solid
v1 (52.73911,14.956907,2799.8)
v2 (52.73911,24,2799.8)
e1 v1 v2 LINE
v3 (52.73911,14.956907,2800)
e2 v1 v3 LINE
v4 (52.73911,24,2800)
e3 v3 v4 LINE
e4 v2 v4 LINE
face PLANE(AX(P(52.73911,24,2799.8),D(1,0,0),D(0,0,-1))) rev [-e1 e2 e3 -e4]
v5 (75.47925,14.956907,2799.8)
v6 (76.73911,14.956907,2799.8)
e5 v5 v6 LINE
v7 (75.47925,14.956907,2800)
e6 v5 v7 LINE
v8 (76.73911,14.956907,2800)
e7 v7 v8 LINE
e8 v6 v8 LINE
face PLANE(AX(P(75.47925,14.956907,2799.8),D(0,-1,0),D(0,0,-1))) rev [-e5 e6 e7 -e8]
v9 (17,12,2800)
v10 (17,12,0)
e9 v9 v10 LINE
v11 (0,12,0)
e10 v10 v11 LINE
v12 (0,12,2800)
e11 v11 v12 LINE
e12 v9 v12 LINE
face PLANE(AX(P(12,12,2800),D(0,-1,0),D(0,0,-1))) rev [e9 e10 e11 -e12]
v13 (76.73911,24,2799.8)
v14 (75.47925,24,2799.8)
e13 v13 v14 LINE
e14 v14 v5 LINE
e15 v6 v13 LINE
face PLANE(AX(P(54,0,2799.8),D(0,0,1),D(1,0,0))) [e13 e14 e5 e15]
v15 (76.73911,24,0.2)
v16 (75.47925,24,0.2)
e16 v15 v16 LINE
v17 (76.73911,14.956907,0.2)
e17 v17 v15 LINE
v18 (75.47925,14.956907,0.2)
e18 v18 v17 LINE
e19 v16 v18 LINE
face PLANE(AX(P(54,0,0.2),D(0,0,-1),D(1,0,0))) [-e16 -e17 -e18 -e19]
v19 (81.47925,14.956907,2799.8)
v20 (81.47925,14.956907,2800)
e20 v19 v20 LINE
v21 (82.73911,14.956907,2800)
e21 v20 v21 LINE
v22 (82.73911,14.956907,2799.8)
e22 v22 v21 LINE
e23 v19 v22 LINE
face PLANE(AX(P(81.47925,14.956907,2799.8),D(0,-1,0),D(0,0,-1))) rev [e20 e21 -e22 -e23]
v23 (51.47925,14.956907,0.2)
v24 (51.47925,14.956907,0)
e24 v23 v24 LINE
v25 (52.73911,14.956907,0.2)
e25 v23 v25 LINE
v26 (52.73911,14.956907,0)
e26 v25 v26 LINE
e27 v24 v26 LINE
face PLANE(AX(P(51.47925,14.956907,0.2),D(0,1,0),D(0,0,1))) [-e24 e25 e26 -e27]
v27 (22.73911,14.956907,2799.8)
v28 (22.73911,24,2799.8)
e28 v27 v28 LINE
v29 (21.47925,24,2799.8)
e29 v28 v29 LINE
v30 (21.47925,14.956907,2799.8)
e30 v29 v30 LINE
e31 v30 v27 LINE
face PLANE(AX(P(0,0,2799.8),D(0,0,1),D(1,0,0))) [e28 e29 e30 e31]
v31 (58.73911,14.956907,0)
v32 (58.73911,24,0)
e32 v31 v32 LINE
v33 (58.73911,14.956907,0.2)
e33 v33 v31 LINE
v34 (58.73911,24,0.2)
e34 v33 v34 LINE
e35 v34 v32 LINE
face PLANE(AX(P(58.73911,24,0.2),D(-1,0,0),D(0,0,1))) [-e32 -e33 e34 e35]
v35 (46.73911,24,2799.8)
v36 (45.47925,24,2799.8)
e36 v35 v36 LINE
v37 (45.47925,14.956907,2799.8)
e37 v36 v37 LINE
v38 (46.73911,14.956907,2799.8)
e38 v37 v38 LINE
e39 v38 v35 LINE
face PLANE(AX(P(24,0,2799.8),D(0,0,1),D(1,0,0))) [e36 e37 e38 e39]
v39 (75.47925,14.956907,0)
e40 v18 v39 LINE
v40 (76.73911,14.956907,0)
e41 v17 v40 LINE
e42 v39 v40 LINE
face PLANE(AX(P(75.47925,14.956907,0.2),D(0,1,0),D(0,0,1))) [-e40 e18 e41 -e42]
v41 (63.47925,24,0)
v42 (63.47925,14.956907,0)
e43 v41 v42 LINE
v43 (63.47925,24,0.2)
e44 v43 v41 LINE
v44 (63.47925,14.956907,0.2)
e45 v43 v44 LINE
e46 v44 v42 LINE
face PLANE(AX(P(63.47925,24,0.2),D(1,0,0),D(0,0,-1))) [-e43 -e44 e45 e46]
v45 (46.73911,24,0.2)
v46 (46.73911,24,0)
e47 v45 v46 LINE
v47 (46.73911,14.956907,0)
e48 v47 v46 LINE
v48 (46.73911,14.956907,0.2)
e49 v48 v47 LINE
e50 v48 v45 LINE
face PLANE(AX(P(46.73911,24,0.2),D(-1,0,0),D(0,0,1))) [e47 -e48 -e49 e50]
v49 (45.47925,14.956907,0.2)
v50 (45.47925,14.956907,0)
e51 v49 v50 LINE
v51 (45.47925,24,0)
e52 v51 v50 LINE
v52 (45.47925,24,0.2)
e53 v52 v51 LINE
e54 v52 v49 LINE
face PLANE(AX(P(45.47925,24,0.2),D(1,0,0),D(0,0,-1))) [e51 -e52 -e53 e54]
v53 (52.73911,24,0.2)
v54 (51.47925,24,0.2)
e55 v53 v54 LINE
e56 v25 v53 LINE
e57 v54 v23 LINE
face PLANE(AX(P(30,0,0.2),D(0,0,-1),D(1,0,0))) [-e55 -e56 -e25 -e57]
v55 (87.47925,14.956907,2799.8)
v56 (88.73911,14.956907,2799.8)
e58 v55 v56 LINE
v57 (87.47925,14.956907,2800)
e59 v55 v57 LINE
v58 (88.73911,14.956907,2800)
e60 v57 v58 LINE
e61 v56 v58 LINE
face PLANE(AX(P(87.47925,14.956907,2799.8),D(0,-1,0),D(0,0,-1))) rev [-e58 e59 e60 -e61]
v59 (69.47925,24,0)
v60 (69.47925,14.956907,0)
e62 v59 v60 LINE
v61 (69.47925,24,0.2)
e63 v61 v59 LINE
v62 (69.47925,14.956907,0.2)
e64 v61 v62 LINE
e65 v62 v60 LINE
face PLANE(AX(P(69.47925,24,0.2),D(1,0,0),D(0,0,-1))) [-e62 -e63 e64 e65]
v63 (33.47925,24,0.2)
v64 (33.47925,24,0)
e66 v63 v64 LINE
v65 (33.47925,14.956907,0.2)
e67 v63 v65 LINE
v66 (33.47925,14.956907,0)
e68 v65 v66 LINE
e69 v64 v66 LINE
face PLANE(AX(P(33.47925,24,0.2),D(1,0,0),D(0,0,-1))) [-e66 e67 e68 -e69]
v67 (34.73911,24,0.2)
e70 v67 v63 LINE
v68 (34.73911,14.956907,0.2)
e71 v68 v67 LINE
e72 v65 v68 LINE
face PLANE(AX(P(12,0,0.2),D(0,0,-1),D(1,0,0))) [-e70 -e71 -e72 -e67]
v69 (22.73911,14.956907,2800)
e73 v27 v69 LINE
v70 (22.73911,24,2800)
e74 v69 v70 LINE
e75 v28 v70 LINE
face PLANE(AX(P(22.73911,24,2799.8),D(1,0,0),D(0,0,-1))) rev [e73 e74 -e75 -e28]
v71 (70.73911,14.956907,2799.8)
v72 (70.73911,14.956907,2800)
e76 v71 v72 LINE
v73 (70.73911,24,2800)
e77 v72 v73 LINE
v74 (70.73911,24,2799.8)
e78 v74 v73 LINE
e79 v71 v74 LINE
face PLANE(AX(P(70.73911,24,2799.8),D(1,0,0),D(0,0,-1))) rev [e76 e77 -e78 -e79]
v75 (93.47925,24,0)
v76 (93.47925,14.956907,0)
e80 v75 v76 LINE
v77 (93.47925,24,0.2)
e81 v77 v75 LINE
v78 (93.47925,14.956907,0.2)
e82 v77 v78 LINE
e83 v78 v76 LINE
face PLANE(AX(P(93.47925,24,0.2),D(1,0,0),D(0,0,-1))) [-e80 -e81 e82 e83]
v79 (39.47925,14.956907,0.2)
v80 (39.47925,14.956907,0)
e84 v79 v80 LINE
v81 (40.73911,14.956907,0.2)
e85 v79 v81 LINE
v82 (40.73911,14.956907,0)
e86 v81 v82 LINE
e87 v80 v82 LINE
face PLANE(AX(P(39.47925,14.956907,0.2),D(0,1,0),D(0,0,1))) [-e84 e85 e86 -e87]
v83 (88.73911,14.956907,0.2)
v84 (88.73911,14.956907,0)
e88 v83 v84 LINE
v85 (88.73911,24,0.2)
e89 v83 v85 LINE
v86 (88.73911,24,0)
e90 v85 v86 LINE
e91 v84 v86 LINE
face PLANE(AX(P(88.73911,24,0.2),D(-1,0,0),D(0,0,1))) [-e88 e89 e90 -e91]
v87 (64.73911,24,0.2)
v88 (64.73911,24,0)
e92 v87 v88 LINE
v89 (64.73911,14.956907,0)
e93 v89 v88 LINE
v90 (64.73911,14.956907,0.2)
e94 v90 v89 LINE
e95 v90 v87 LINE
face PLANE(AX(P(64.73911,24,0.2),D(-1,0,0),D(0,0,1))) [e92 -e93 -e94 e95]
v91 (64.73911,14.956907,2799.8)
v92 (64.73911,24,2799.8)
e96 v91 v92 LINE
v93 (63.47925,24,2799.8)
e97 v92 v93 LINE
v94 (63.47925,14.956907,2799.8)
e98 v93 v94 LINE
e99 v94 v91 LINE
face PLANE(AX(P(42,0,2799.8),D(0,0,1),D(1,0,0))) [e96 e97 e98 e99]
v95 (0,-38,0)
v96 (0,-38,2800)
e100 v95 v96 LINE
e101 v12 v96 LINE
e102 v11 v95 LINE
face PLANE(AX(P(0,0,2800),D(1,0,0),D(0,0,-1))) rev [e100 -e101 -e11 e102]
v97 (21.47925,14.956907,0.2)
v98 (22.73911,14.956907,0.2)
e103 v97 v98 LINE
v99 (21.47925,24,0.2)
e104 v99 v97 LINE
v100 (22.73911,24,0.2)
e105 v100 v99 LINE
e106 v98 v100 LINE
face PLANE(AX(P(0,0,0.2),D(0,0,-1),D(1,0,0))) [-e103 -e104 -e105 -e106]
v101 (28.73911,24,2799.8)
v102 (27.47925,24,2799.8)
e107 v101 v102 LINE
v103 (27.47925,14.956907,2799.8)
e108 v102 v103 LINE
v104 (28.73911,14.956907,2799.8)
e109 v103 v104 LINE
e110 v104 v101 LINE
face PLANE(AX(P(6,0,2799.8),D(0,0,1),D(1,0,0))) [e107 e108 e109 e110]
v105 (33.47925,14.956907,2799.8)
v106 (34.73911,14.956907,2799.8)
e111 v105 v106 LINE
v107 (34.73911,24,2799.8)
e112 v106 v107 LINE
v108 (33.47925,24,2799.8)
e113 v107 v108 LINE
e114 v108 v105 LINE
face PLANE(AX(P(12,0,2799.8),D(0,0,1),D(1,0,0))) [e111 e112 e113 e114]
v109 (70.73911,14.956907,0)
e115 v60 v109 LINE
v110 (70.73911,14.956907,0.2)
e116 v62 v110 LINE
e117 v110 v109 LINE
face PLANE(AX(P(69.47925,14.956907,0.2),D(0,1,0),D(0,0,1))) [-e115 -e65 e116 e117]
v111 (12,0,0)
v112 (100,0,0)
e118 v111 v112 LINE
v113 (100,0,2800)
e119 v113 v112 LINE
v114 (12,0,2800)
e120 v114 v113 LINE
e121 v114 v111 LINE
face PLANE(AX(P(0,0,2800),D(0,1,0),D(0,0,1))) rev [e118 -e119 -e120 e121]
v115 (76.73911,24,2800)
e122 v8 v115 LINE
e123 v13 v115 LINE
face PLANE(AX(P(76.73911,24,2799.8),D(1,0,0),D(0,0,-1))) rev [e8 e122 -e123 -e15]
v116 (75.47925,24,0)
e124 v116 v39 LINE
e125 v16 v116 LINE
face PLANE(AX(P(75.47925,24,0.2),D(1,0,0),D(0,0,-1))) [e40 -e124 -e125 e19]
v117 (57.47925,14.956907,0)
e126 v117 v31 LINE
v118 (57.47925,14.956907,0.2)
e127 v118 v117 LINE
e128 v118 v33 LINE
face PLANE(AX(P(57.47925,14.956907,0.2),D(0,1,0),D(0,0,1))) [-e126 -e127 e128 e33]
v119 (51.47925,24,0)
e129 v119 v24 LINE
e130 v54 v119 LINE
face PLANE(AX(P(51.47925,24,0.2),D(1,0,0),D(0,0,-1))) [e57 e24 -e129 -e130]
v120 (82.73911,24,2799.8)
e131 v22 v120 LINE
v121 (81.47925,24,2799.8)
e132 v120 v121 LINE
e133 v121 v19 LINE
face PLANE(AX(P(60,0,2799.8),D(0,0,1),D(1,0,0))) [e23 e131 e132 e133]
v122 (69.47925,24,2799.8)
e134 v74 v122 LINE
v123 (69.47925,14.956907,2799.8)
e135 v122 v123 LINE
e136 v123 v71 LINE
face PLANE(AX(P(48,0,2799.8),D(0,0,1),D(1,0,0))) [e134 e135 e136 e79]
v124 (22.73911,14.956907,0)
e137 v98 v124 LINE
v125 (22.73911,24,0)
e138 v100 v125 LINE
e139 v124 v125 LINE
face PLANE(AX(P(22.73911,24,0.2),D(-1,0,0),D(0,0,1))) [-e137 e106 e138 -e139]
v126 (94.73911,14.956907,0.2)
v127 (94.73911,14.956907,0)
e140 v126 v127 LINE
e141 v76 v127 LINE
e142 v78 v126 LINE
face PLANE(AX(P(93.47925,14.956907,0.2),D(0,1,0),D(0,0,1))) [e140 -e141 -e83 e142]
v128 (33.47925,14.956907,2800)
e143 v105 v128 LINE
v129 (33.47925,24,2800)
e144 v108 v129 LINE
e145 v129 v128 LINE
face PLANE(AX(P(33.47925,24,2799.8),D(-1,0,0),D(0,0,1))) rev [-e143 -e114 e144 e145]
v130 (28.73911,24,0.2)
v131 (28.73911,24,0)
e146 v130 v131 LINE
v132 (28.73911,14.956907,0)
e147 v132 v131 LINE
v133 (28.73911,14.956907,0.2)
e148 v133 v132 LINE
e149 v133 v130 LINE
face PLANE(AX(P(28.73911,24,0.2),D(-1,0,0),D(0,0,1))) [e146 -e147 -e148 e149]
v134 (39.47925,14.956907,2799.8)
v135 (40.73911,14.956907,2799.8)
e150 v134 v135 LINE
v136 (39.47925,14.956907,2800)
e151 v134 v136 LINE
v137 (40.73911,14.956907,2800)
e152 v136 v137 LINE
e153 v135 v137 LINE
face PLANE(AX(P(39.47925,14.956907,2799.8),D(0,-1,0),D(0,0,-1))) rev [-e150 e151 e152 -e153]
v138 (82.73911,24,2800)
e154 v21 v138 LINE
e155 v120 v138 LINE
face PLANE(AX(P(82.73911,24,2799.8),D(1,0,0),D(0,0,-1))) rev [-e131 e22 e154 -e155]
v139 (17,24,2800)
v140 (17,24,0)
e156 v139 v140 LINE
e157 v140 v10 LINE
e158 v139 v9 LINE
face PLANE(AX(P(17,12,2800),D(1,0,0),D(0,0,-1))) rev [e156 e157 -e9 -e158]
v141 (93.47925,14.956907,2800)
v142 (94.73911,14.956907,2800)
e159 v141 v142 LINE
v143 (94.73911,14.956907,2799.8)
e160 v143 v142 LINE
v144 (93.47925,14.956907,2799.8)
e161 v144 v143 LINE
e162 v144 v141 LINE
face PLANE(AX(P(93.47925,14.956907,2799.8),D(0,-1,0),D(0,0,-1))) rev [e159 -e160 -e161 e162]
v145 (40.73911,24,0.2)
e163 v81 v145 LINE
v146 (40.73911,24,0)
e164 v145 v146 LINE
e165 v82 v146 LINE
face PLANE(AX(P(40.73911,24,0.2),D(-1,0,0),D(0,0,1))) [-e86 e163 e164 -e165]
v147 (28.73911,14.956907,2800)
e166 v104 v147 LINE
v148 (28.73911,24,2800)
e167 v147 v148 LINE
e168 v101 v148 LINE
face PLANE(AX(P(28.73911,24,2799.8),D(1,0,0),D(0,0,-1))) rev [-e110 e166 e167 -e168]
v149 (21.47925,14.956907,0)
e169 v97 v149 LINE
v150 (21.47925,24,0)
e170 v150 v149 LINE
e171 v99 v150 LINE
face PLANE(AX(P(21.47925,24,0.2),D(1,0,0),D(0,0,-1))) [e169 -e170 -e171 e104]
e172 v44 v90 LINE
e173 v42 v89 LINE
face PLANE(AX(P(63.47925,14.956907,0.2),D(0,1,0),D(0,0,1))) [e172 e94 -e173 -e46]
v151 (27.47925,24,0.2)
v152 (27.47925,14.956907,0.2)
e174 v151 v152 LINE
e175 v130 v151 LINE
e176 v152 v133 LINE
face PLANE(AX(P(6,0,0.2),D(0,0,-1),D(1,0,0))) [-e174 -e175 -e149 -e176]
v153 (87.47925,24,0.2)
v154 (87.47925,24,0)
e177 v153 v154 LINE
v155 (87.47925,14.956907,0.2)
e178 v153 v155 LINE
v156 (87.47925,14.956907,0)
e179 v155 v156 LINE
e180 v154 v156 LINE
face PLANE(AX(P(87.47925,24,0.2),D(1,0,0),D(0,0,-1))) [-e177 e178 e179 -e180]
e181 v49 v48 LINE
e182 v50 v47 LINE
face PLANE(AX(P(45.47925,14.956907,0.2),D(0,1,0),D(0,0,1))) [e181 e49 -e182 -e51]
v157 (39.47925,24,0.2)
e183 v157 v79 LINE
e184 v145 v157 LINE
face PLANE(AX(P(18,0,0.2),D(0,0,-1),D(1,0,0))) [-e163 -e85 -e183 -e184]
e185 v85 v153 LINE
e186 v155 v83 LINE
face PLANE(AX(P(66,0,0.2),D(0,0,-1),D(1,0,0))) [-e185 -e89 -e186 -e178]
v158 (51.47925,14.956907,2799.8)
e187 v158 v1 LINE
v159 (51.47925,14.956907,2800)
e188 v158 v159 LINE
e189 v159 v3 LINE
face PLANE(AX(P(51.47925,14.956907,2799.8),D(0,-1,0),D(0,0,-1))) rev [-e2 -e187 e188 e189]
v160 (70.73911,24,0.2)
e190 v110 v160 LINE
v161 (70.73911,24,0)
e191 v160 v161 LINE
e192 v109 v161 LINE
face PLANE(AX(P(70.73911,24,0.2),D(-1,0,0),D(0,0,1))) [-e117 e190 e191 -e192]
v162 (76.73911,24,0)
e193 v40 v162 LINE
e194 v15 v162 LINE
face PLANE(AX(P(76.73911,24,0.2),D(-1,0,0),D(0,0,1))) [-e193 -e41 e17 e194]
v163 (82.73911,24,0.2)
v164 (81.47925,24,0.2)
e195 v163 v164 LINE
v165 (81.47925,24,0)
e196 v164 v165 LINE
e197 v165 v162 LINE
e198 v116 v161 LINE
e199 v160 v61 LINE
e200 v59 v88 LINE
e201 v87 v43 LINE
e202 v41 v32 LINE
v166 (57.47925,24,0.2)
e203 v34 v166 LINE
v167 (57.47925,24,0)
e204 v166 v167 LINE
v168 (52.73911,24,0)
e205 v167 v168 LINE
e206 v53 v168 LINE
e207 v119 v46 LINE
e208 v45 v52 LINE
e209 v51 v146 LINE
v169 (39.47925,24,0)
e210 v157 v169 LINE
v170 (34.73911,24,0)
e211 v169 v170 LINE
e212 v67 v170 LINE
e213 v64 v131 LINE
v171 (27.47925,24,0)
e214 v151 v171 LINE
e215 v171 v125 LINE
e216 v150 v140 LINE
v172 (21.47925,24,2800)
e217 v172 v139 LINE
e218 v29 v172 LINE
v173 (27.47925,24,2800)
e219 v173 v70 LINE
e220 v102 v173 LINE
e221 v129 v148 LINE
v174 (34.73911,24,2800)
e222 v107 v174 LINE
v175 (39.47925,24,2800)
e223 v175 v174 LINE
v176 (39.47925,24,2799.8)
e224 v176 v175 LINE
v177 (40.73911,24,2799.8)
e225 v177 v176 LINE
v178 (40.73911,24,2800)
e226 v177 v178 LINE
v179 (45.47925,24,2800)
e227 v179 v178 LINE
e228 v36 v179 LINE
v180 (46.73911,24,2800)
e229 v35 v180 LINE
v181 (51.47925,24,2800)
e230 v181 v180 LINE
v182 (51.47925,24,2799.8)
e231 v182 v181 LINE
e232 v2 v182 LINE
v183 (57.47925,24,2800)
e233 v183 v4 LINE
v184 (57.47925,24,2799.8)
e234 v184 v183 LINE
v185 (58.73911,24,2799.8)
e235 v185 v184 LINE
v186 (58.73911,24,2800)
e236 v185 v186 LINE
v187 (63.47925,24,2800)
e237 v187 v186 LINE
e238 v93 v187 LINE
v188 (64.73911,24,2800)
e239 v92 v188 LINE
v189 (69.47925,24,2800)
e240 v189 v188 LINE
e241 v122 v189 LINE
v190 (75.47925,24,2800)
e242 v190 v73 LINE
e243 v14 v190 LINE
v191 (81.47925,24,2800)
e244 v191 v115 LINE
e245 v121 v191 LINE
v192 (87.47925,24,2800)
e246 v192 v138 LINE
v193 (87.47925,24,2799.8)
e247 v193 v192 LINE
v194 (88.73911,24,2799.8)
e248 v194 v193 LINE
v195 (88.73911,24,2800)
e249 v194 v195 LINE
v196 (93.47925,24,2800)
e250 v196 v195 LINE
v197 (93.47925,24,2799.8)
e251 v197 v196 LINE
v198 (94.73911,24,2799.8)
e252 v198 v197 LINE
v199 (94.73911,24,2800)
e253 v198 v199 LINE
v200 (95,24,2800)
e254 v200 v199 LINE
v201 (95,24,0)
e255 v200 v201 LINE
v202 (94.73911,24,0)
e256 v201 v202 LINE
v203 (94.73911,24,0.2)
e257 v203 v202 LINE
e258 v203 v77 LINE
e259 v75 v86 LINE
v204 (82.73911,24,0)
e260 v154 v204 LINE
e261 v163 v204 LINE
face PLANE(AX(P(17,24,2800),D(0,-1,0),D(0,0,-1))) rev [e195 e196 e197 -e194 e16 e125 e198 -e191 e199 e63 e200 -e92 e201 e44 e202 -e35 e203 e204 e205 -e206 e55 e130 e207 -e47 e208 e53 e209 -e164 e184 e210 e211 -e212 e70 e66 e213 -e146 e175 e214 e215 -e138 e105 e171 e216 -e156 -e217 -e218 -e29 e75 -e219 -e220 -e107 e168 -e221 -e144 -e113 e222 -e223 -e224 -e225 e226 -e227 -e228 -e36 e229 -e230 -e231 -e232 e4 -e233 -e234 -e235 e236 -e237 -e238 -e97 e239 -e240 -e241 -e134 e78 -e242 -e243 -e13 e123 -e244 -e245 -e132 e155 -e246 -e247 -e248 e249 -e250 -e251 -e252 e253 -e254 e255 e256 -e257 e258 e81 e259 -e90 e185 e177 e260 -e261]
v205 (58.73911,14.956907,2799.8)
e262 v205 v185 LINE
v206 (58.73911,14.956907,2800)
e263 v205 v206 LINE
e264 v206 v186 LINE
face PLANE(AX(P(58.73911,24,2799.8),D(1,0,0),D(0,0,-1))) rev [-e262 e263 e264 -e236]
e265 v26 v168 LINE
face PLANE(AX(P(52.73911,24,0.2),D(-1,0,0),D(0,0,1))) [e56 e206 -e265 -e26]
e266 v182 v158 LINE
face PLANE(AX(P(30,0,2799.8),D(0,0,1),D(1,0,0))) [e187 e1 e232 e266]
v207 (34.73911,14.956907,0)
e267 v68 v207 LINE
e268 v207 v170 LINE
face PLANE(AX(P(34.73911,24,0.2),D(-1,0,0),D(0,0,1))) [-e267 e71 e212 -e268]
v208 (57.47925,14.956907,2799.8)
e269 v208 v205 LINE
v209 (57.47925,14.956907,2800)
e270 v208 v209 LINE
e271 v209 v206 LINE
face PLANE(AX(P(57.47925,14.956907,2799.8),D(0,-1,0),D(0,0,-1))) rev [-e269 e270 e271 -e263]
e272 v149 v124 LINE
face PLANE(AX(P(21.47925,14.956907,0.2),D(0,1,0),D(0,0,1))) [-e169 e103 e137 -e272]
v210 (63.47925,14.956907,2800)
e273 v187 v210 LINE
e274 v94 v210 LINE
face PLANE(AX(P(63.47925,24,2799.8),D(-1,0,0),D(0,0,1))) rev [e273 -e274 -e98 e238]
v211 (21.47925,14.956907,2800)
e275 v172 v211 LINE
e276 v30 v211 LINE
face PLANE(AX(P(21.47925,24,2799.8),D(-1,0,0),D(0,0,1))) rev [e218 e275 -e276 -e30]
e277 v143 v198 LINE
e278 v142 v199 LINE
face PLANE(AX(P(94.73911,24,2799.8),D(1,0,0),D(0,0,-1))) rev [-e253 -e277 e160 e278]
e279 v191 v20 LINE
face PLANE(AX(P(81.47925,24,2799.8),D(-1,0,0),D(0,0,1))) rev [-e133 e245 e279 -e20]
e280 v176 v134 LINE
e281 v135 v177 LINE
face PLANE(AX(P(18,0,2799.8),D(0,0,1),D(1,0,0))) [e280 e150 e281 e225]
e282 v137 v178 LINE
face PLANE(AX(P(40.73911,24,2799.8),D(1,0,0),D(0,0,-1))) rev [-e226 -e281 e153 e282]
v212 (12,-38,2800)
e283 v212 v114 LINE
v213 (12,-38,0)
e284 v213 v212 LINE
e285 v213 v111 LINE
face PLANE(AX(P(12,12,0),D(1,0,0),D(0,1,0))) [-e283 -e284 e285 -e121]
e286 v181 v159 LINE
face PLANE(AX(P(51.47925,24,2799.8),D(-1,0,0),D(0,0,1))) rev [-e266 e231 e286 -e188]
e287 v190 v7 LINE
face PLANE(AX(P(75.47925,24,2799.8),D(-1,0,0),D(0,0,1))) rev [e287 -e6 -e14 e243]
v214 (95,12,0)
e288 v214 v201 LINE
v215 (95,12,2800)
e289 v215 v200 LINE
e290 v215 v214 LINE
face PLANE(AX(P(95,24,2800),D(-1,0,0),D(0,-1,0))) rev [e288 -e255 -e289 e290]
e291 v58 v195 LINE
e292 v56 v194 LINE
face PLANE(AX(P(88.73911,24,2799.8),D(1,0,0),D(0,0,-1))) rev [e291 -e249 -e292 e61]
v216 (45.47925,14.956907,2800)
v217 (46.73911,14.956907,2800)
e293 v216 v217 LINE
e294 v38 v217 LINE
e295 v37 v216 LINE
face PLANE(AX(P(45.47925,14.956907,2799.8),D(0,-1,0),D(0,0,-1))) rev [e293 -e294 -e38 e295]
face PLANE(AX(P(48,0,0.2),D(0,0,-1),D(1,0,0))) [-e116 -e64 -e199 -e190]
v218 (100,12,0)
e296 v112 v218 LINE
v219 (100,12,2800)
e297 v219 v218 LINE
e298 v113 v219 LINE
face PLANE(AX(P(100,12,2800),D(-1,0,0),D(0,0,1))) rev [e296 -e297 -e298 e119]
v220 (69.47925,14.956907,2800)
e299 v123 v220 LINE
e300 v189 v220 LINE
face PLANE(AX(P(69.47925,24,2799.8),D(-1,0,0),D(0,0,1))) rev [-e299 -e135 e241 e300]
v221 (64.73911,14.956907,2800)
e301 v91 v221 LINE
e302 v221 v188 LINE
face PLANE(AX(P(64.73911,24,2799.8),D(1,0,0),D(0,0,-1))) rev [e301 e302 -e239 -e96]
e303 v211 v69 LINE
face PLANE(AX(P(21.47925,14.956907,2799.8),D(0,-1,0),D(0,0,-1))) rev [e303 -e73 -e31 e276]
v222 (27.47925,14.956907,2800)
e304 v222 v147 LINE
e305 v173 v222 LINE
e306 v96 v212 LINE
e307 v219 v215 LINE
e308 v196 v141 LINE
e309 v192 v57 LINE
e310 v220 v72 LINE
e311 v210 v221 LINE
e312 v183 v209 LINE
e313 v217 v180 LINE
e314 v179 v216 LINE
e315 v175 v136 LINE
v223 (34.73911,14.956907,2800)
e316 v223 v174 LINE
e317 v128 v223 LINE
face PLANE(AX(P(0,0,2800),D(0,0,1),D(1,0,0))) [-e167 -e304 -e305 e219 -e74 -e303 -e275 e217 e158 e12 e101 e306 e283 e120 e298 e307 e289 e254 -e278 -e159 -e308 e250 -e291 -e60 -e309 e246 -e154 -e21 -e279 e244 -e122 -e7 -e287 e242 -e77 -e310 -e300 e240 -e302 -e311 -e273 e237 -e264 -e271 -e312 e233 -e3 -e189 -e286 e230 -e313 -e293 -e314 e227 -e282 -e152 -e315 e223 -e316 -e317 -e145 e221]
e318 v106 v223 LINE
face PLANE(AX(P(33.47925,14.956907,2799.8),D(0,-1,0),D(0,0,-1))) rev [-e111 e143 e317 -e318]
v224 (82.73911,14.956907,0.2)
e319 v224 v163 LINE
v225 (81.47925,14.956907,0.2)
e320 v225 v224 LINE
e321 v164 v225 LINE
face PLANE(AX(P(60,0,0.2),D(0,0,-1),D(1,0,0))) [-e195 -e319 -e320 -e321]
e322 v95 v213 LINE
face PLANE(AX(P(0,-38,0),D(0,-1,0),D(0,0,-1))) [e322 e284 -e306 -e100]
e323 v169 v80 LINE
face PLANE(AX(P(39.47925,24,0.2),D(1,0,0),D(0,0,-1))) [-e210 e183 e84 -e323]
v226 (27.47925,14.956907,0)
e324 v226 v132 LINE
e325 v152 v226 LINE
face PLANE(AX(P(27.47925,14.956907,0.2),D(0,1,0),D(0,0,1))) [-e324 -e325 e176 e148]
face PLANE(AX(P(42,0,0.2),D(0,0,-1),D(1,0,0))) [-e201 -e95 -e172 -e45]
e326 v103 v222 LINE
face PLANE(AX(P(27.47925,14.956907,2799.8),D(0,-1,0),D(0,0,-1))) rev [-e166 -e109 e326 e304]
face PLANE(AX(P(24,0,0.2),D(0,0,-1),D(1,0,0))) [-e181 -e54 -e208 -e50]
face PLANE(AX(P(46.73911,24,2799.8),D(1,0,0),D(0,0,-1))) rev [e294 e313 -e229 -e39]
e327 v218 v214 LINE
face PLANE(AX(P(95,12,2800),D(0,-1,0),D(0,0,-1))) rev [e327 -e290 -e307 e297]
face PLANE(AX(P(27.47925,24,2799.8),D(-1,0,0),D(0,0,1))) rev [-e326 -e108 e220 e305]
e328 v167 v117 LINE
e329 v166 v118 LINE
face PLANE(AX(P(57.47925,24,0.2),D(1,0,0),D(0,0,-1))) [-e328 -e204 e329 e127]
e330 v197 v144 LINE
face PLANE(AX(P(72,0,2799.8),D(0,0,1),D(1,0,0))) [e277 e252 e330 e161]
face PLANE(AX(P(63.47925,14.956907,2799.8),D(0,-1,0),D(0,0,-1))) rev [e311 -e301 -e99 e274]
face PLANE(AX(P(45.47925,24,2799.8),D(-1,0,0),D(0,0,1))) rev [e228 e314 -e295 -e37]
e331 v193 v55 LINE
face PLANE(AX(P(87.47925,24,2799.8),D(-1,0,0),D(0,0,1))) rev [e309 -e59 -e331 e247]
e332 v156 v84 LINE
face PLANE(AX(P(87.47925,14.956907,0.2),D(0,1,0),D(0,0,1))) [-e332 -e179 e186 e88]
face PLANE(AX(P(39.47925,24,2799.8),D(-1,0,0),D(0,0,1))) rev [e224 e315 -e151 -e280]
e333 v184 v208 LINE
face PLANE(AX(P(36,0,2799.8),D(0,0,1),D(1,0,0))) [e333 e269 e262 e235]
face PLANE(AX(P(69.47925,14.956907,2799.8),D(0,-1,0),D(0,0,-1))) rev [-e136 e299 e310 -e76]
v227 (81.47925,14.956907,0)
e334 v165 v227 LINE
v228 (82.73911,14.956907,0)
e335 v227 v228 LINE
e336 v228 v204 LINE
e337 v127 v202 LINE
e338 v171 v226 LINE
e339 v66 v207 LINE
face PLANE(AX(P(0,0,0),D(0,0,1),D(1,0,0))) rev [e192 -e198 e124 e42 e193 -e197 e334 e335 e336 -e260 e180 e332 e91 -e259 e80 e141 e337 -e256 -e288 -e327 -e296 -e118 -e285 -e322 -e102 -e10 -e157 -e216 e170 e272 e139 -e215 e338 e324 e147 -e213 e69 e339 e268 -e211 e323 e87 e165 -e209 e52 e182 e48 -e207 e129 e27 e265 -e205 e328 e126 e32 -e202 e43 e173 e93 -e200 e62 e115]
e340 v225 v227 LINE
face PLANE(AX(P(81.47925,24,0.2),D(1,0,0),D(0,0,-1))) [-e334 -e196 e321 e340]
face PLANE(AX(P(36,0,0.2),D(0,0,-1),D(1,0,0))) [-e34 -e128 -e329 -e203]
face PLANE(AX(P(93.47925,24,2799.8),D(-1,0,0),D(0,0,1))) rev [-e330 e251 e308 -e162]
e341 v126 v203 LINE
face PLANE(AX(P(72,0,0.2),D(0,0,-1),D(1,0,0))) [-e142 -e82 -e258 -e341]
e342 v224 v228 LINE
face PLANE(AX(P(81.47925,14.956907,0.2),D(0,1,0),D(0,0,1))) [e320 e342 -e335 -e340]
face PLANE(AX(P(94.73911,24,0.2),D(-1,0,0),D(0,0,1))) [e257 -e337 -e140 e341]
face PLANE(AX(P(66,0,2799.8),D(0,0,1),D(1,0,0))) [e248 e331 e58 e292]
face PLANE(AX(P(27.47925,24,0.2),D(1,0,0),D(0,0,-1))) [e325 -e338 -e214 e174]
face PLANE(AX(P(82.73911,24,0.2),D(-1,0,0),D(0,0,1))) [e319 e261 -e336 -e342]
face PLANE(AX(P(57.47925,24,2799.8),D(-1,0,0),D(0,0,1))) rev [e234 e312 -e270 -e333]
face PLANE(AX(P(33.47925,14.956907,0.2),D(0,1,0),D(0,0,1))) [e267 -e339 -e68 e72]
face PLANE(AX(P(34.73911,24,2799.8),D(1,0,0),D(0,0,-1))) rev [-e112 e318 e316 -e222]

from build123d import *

# Parameters (mm, degrees)
BOSS_EXTRUDE1_DEPTH      = 2800
SKETCH2_W                = 1.259860676
SKETCH2_H                = 9.043092937
CUT_EXTRUDE1_DEPTH       = 0.2
LPATTERN1_COUNT          = 16
LPATTERN1_PITCH          = 6
MIRROR1_COPY_1_SKETCH_W  = 1.259860676
MIRROR1_COPY_1_SKETCH_H  = 9.043092937
MIRROR1_COPY_1_DEPTH     = 0.2
MIRROR1_COPY_2_SKETCH_W  = 1.259860676
MIRROR1_COPY_2_SKETCH_H  = 9.043092937
MIRROR1_COPY_2_DEPTH     = 0.2
MIRROR1_COPY_3_SKETCH_W  = 1.259860676
MIRROR1_COPY_3_SKETCH_H  = 9.043092937
MIRROR1_COPY_3_DEPTH     = 0.2
MIRROR1_COPY_4_SKETCH_W  = 1.259860676
MIRROR1_COPY_4_SKETCH_H  = 9.043092937
MIRROR1_COPY_4_DEPTH     = 0.2
MIRROR1_COPY_5_SKETCH_W  = 1.259860676
MIRROR1_COPY_5_SKETCH_H  = 9.043092937
MIRROR1_COPY_5_DEPTH     = 0.2
MIRROR1_COPY_6_SKETCH_W  = 1.259860676
MIRROR1_COPY_6_SKETCH_H  = 9.043092937
MIRROR1_COPY_6_DEPTH     = 0.2
MIRROR1_COPY_7_SKETCH_W  = 1.259860676
MIRROR1_COPY_7_SKETCH_H  = 9.043092937
MIRROR1_COPY_7_DEPTH     = 0.2
MIRROR1_COPY_8_SKETCH_W  = 1.259860676
MIRROR1_COPY_8_SKETCH_H  = 9.043092937
MIRROR1_COPY_8_DEPTH     = 0.2
MIRROR1_COPY_9_SKETCH_W  = 1.259860676
MIRROR1_COPY_9_SKETCH_H  = 9.043092937
MIRROR1_COPY_9_DEPTH     = 0.2
MIRROR1_COPY_10_SKETCH_W = 1.259860676
MIRROR1_COPY_10_SKETCH_H = 9.043092937
MIRROR1_COPY_10_DEPTH    = 0.2
MIRROR1_COPY_11_SKETCH_W = 1.259860676
MIRROR1_COPY_11_SKETCH_H = 9.043092937
MIRROR1_COPY_11_DEPTH    = 0.2
MIRROR1_COPY_12_SKETCH_W = 1.259860676
MIRROR1_COPY_12_SKETCH_H = 9.043092937
MIRROR1_COPY_12_DEPTH    = 0.2
MIRROR1_COPY_13_SKETCH_W = 1.259860676
MIRROR1_COPY_13_SKETCH_H = 9.043092937
MIRROR1_COPY_13_DEPTH    = 0.2
MIRROR1_COPY_14_SKETCH_W = 1.259860676
MIRROR1_COPY_14_SKETCH_H = 9.043092937
MIRROR1_COPY_14_DEPTH    = 0.2
MIRROR1_COPY_15_SKETCH_W = 1.259860676
MIRROR1_COPY_15_SKETCH_H = 9.043092937
MIRROR1_COPY_15_DEPTH    = 0.2
SKETCH5_W                = 12
SKETCH5_H                = 50
BOSS_EXTRUDE2_DEPTH      = 2800
SKETCH3_W                = 12
SKETCH3_H                = 88
CUT_EXTRUDE3_DEPTH       = 2804.569153775


with BuildPart() as part:
    # Sketch1 → Boss-Extrude1 (new body)
    with BuildSketch(Plane.XY):
        Polygon((0, 0), (100, 0), (100, 12), (95, 12), (95, 24), (17, 24), (17, 12), (12, 12), (12, 100), (0, 100), align=None)
    extrude(amount=BOSS_EXTRUDE1_DEPTH)

    # Sketch2 → Cut-Extrude1 (cut)
    with BuildSketch(Plane.XY.offset(2800)):
        with Locations((22.109179897, 19.478453532)):
            Rectangle(SKETCH2_W, SKETCH2_H)
    cut_extrude1 = extrude(amount=-CUT_EXTRUDE1_DEPTH, mode=Mode.SUBTRACT)

    # LPattern1: Cut-Extrude1 ×16
    with Locations(*[(i * LPATTERN1_PITCH, 0, 0) for i in range(1, LPATTERN1_COUNT)]):
        add(cut_extrude1, mode=Mode.SUBTRACT)

    # Mirror1: Cut-Extrude1 across plane
    add(cut_extrude1.mirror(Plane(origin=(0, 0, 1400), x_dir=(1, 0, 0), z_dir=(0, 0, -1))), mode=Mode.SUBTRACT)

    # Mirror1 copy 1 sketch → Mirror1 copy 1 (cut)
    with BuildSketch(Plane(origin=(6, 0, 0), x_dir=(1, 0, 0), z_dir=(0, 0, -1))):
        with Locations((22.109179897, -19.478453532)):
            Rectangle(MIRROR1_COPY_1_SKETCH_W, MIRROR1_COPY_1_SKETCH_H)
    extrude(amount=-MIRROR1_COPY_1_DEPTH, mode=Mode.SUBTRACT)

    # Mirror1 copy 2 sketch → Mirror1 copy 2 (cut)
    with BuildSketch(Plane(origin=(12, 0, 0), x_dir=(1, 0, 0), z_dir=(0, 0, -1))):
        with Locations((22.109179897, -19.478453532)):
            Rectangle(MIRROR1_COPY_2_SKETCH_W, MIRROR1_COPY_2_SKETCH_H)
    extrude(amount=-MIRROR1_COPY_2_DEPTH, mode=Mode.SUBTRACT)

    # Mirror1 copy 3 sketch → Mirror1 copy 3 (cut)
    with BuildSketch(Plane(origin=(18, 0, 0), x_dir=(1, 0, 0), z_dir=(0, 0, -1))):
        with Locations((22.109179897, -19.478453532)):
            Rectangle(MIRROR1_COPY_3_SKETCH_W, MIRROR1_COPY_3_SKETCH_H)
    extrude(amount=-MIRROR1_COPY_3_DEPTH, mode=Mode.SUBTRACT)

    # Mirror1 copy 4 sketch → Mirror1 copy 4 (cut)
    with BuildSketch(Plane(origin=(24, 0, 0), x_dir=(1, 0, 0), z_dir=(0, 0, -1))):
        with Locations((22.109179897, -19.478453532)):
            Rectangle(MIRROR1_COPY_4_SKETCH_W, MIRROR1_COPY_4_SKETCH_H)
    extrude(amount=-MIRROR1_COPY_4_DEPTH, mode=Mode.SUBTRACT)

    # Mirror1 copy 5 sketch → Mirror1 copy 5 (cut)
    with BuildSketch(Plane(origin=(30, 0, 0), x_dir=(1, 0, 0), z_dir=(0, 0, -1))):
        with Locations((22.109179897, -19.478453532)):
            Rectangle(MIRROR1_COPY_5_SKETCH_W, MIRROR1_COPY_5_SKETCH_H)
    extrude(amount=-MIRROR1_COPY_5_DEPTH, mode=Mode.SUBTRACT)

    # Mirror1 copy 6 sketch → Mirror1 copy 6 (cut)
    with BuildSketch(Plane(origin=(36, 0, 0), x_dir=(1, 0, 0), z_dir=(0, 0, -1))):
        with Locations((22.109179897, -19.478453532)):
            Rectangle(MIRROR1_COPY_6_SKETCH_W, MIRROR1_COPY_6_SKETCH_H)
    extrude(amount=-MIRROR1_COPY_6_DEPTH, mode=Mode.SUBTRACT)

    # Mirror1 copy 7 sketch → Mirror1 copy 7 (cut)
    with BuildSketch(Plane(origin=(42, 0, 0), x_dir=(1, 0, 0), z_dir=(0, 0, -1))):
        with Locations((22.109179897, -19.478453532)):
            Rectangle(MIRROR1_COPY_7_SKETCH_W, MIRROR1_COPY_7_SKETCH_H)
    extrude(amount=-MIRROR1_COPY_7_DEPTH, mode=Mode.SUBTRACT)

    # Mirror1 copy 8 sketch → Mirror1 copy 8 (cut)
    with BuildSketch(Plane(origin=(48, 0, 0), x_dir=(1, 0, 0), z_dir=(0, 0, -1))):
        with Locations((22.109179897, -19.478453532)):
            Rectangle(MIRROR1_COPY_8_SKETCH_W, MIRROR1_COPY_8_SKETCH_H)
    extrude(amount=-MIRROR1_COPY_8_DEPTH, mode=Mode.SUBTRACT)

    # Mirror1 copy 9 sketch → Mirror1 copy 9 (cut)
    with BuildSketch(Plane(origin=(54, 0, 0), x_dir=(1, 0, 0), z_dir=(0, 0, -1))):
        with Locations((22.109179897, -19.478453532)):
            Rectangle(MIRROR1_COPY_9_SKETCH_W, MIRROR1_COPY_9_SKETCH_H)
    extrude(amount=-MIRROR1_COPY_9_DEPTH, mode=Mode.SUBTRACT)

    # Mirror1 copy 10 sketch → Mirror1 copy 10 (cut)
    with BuildSketch(Plane(origin=(60, 0, 0), x_dir=(1, 0, 0), z_dir=(0, 0, -1))):
        with Locations((22.109179897, -19.478453532)):
            Rectangle(MIRROR1_COPY_10_SKETCH_W, MIRROR1_COPY_10_SKETCH_H)
    extrude(amount=-MIRROR1_COPY_10_DEPTH, mode=Mode.SUBTRACT)

    # Mirror1 copy 11 sketch → Mirror1 copy 11 (cut)
    with BuildSketch(Plane(origin=(66, 0, 0), x_dir=(1, 0, 0), z_dir=(0, 0, -1))):
        with Locations((22.109179897, -19.478453532)):
            Rectangle(MIRROR1_COPY_11_SKETCH_W, MIRROR1_COPY_11_SKETCH_H)
    extrude(amount=-MIRROR1_COPY_11_DEPTH, mode=Mode.SUBTRACT)

    # Mirror1 copy 12 sketch → Mirror1 copy 12 (cut)
    with BuildSketch(Plane(origin=(72, 0, 0), x_dir=(1, 0, 0), z_dir=(0, 0, -1))):
        with Locations((22.109179897, -19.478453532)):
            Rectangle(MIRROR1_COPY_12_SKETCH_W, MIRROR1_COPY_12_SKETCH_H)
    extrude(amount=-MIRROR1_COPY_12_DEPTH, mode=Mode.SUBTRACT)

    # Mirror1 copy 13 sketch → Mirror1 copy 13 (cut)
    with BuildSketch(Plane(origin=(78, 0, 0), x_dir=(1, 0, 0), z_dir=(0, 0, -1))):
        with Locations((22.109179897, -19.478453532)):
            Rectangle(MIRROR1_COPY_13_SKETCH_W, MIRROR1_COPY_13_SKETCH_H)
    extrude(amount=-MIRROR1_COPY_13_DEPTH, mode=Mode.SUBTRACT)

    # Mirror1 copy 14 sketch → Mirror1 copy 14 (cut)
    with BuildSketch(Plane(origin=(84, 0, 0), x_dir=(1, 0, 0), z_dir=(0, 0, -1))):
        with Locations((22.109179897, -19.478453532)):
            Rectangle(MIRROR1_COPY_14_SKETCH_W, MIRROR1_COPY_14_SKETCH_H)
    extrude(amount=-MIRROR1_COPY_14_DEPTH, mode=Mode.SUBTRACT)

    # Mirror1 copy 15 sketch → Mirror1 copy 15 (cut)
    with BuildSketch(Plane(origin=(90, 0, 0), x_dir=(1, 0, 0), z_dir=(0, 0, -1))):
        with Locations((22.109179897, -19.478453532)):
            Rectangle(MIRROR1_COPY_15_SKETCH_W, MIRROR1_COPY_15_SKETCH_H)
    extrude(amount=-MIRROR1_COPY_15_DEPTH, mode=Mode.SUBTRACT)

    # Sketch5 → Boss-Extrude2 (add)
    with BuildSketch(Plane.XY.offset(2800)):
        with Locations((6, -13)):
            Rectangle(SKETCH5_W, SKETCH5_H)
    extrude(amount=-BOSS_EXTRUDE2_DEPTH)

    # Sketch3 → Cut-Extrude3 (cut, through all)
    with BuildSketch(Plane.XY.offset(2800)):
        with Locations((6, 56)):
            Rectangle(SKETCH3_W, SKETCH3_H)
    extrude(amount=-CUT_EXTRUDE3_DEPTH, mode=Mode.SUBTRACT)


solid = part.part
